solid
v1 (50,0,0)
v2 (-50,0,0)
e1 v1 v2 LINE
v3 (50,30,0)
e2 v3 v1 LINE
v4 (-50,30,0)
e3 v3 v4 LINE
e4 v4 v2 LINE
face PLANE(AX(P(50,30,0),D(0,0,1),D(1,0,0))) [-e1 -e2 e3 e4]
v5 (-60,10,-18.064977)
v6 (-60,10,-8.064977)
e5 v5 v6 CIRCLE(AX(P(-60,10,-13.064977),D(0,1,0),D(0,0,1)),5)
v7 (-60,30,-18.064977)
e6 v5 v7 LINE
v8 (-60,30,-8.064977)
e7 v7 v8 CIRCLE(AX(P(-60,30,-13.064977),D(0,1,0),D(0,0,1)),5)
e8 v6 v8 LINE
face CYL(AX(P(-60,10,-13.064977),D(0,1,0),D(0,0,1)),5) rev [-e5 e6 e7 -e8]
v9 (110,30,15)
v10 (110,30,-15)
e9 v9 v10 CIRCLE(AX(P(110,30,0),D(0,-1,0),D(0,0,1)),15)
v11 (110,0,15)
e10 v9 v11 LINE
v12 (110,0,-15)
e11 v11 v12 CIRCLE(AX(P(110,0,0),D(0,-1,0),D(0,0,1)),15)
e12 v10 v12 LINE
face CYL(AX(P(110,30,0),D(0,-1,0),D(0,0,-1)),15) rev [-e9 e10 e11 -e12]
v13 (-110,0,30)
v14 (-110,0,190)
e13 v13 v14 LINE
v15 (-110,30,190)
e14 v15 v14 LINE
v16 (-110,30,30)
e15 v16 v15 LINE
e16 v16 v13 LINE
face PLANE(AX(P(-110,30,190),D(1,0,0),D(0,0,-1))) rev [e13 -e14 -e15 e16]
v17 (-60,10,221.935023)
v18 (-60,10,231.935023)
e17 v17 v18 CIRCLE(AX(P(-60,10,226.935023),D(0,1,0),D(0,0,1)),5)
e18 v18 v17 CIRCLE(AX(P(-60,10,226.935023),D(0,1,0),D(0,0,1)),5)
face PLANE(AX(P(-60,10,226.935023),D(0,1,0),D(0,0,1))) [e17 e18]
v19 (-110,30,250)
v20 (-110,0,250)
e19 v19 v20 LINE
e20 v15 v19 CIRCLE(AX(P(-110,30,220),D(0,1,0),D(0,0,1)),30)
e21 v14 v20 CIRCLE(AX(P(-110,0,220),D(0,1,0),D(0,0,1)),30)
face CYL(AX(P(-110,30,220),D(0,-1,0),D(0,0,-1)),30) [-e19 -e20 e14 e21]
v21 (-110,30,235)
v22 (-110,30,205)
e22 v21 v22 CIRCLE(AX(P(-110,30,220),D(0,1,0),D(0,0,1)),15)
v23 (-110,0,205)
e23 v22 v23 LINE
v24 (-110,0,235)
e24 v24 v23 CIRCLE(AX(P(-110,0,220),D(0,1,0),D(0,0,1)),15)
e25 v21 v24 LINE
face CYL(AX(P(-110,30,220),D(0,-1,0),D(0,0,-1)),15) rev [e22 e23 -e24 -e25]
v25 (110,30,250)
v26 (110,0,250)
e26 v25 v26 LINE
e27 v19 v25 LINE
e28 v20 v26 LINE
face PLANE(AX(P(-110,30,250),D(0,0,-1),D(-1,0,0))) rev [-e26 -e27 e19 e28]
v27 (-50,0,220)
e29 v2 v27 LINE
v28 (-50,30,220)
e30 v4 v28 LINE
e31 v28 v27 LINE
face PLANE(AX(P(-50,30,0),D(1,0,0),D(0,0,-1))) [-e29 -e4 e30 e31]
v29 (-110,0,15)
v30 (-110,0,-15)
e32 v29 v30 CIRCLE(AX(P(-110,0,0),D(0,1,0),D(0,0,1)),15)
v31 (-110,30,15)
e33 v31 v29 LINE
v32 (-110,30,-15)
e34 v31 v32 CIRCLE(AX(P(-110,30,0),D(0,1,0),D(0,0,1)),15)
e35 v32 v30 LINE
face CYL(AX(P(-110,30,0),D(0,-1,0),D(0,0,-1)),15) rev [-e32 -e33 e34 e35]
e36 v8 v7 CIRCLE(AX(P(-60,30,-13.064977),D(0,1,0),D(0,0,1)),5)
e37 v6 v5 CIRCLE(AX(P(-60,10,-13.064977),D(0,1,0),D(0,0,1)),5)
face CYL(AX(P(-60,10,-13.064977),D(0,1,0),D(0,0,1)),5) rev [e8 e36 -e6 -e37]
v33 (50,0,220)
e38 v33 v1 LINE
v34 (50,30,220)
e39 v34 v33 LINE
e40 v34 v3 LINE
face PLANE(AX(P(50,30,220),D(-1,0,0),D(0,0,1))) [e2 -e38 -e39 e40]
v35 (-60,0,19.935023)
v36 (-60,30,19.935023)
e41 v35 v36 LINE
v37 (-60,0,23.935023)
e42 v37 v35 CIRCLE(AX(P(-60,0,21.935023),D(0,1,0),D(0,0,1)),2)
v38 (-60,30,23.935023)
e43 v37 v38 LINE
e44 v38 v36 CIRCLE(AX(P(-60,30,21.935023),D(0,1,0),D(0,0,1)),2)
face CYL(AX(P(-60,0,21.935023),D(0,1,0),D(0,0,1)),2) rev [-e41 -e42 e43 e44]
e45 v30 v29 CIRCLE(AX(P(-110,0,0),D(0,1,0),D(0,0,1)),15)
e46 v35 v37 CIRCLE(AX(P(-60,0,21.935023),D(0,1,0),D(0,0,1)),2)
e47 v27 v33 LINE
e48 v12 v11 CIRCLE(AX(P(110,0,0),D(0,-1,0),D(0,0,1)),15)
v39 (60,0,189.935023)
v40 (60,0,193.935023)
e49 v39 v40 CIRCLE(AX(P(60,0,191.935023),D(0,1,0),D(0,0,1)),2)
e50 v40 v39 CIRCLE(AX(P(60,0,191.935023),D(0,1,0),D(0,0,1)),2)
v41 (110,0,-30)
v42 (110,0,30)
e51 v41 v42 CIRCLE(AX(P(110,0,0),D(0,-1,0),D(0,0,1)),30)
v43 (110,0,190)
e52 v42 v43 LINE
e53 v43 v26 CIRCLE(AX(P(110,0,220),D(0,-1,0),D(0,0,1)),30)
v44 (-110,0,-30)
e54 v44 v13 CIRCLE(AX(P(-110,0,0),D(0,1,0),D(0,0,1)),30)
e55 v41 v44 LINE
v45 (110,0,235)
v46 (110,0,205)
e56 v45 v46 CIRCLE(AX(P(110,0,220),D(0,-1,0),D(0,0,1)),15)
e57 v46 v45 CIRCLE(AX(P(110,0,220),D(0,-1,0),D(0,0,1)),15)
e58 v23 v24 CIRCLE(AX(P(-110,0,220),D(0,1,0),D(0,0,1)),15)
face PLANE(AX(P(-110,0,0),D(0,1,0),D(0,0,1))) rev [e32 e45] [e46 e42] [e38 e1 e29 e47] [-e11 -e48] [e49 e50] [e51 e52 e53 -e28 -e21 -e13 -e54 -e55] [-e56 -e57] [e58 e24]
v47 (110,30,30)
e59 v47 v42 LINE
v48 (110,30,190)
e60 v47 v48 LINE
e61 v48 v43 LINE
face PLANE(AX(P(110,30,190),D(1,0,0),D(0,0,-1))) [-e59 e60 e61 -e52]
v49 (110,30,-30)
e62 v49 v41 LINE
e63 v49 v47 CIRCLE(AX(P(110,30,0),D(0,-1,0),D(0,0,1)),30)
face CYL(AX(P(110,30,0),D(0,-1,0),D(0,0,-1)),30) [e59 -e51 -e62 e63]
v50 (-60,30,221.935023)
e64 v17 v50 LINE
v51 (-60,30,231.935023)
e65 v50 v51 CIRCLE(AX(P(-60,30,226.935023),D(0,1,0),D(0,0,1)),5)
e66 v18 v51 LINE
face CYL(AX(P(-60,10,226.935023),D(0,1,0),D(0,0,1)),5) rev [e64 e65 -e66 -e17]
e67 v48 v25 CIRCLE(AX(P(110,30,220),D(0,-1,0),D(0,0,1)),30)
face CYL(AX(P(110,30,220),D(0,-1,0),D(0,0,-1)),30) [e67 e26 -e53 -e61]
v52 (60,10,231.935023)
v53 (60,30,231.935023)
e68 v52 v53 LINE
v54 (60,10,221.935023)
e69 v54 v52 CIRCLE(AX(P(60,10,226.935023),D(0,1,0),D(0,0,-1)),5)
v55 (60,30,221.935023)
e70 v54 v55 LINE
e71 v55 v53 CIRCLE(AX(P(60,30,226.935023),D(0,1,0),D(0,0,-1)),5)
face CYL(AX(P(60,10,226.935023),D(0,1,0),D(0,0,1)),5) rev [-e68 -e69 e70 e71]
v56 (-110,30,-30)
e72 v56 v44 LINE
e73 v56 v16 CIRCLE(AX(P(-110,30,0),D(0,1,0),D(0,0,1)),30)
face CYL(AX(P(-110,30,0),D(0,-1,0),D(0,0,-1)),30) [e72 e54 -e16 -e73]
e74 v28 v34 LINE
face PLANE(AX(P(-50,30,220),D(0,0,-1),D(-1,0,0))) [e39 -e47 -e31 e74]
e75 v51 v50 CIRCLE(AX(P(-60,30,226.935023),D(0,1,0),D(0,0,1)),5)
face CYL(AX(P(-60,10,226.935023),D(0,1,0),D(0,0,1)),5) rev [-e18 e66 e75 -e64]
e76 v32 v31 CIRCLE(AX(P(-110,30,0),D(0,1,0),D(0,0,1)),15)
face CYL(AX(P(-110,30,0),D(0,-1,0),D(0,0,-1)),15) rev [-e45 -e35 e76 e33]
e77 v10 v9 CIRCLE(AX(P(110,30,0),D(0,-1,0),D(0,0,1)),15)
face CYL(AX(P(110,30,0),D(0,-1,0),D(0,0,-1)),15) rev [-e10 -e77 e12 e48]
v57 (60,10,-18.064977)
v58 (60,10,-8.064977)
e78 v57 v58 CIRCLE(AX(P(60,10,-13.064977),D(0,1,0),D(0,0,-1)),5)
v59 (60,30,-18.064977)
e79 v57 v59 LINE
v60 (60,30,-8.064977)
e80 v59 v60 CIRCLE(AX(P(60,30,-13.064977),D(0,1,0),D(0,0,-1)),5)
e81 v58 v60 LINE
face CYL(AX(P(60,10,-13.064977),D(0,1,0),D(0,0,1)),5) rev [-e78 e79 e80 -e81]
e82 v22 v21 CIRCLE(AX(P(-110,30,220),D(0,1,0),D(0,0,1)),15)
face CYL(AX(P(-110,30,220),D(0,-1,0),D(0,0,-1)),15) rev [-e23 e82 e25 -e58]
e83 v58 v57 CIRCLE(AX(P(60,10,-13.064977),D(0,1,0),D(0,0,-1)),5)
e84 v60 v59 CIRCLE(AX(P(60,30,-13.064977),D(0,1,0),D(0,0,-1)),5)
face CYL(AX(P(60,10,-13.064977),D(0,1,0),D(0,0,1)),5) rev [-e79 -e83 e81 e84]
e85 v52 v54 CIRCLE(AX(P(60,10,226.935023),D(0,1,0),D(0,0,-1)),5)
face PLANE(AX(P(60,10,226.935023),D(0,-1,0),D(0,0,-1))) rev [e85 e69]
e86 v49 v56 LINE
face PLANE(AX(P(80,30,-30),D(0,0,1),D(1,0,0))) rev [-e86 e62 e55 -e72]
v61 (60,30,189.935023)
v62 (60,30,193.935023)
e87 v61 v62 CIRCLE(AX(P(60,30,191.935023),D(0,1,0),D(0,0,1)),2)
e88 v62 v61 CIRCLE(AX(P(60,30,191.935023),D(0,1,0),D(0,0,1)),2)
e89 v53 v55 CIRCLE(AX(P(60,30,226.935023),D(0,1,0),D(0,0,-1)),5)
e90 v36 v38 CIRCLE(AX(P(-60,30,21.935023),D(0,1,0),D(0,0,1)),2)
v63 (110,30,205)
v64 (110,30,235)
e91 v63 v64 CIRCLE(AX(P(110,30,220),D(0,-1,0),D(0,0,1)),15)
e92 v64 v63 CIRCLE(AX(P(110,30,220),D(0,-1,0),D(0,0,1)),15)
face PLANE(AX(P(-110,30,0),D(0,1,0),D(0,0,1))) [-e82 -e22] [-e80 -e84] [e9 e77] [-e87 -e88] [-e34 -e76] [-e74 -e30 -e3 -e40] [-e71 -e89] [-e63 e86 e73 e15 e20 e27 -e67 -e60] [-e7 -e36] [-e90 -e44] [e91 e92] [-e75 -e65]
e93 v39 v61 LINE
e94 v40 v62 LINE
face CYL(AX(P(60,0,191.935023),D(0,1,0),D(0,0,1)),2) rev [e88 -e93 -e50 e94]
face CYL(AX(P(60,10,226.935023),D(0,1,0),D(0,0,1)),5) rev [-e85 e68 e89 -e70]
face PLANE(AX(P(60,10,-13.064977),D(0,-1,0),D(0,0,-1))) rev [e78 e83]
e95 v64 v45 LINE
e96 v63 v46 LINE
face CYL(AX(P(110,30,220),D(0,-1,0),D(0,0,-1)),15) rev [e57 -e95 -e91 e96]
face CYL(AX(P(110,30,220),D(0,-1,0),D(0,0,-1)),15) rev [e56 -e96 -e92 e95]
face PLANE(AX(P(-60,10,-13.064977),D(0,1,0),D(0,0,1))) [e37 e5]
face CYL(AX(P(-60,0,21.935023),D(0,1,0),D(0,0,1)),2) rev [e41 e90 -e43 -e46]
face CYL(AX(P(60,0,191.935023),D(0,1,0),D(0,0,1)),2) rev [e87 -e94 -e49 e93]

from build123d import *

# Parameters (mm, degrees)
SKETCH1_R                                        = 15
SKETCH1_W                                        = 100
SKETCH1_H                                        = 220
BOSS_EXTRUDE1_DEPTH                              = 30
CBORE_FOR_M8_PAN_HEAD_MACHINE_SCREW3_D           = 9
CBORE_FOR_M8_PAN_HEAD_MACHINE_SCREW3_CBORE_D     = 18
CBORE_FOR_M8_PAN_HEAD_MACHINE_SCREW3_CBORE_DEPTH = 6
SKETCH_1_R                                       = 5
CUT_EXTRUDE1_DEPTH                               = 20
SKETCH2_R                                        = 2
CUT_EXTRUDE2_DEPTH                               = 289.097205818


with BuildPart() as part:
    # Sketch1 → Boss-Extrude1 (new body)
    with BuildSketch(Plane(origin=(0, 0, 0), x_dir=(1, 0, 0), z_dir=(0, 1, 0))):
        with BuildLine():
            Line((-110, -250), (80, -250))
            Line((80, -250), (80, 30))
            Line((80, 30), (-110, 30))
            ThreePointArc((-110, 30), (-140, 0), (-110, -30))
            Line((-110, -30), (-110, -190))
            ThreePointArc((-110, -190), (-140, -220), (-110, -250))
        make_face()
        with Locations(Location((-110, 0, 0), (0, 0, 270))):
            Circle(SKETCH1_R, mode=Mode.SUBTRACT)
        with Locations(Location((-110, -220, 0), (0, 0, 270))):
            Circle(SKETCH1_R, mode=Mode.SUBTRACT)
        with Locations((0, -110)):
            Rectangle(SKETCH1_W, SKETCH1_H, mode=Mode.SUBTRACT)
    boss_extrude1 = extrude(amount=BOSS_EXTRUDE1_DEPTH)

    # CBORE for M8 Pan Head Machine Screw3 (through all)
    with Locations(Plane(origin=(0, 0, 0), x_dir=(-1, 0, 0), z_dir=(0, -1, 0))):
        with Locations((60, -230), (-60, -230), (-60, 10), (60, 10)):
            CounterBoreHole(CBORE_FOR_M8_PAN_HEAD_MACHINE_SCREW3_D / 2, CBORE_FOR_M8_PAN_HEAD_MACHINE_SCREW3_CBORE_D / 2, CBORE_FOR_M8_PAN_HEAD_MACHINE_SCREW3_CBORE_DEPTH)

    # Mirror1: Boss-Extrude1 across plane
    add(boss_extrude1.mirror(Plane(origin=(0, 0, 0), x_dir=(0, 0, 1), z_dir=(1, 0, 0))))

    # 草图1 → Cut-Extrude1 (cut)
    with BuildSketch(Plane(origin=(0, 30, 0), x_dir=(1, 0, 0), z_dir=(0, 1, 0))):
        with Locations(Location((-60, 13.06497659, 0), (0, 0, 270))):
            Circle(SKETCH_1_R)
        with Locations(Location((-60, -226.93502341, 0), (0, 0, 270))):
            Circle(SKETCH_1_R)
        with Locations(Location((60, 13.06497659, 0), (0, 0, 90))):
            Circle(SKETCH_1_R)
        with Locations(Location((60, -226.93502341, 0), (0, 0, 90))):
            Circle(SKETCH_1_R)
    extrude(amount=-CUT_EXTRUDE1_DEPTH, mode=Mode.SUBTRACT)

    # Sketch2 → Cut-Extrude2 (cut, through all)
    with BuildSketch(Plane(origin=(0, 30, 0), x_dir=(1, 0, 0), z_dir=(0, 1, 0))):
        with Locations(Location((-60, -21.93502341, 0), (0, 0, 270))):
            Circle(SKETCH2_R)
        with Locations(Location((60, -191.93502341, 0), (0, 0, 270))):
            Circle(SKETCH2_R)
    extrude(amount=-CUT_EXTRUDE2_DEPTH, mode=Mode.SUBTRACT)


solid = part.part
